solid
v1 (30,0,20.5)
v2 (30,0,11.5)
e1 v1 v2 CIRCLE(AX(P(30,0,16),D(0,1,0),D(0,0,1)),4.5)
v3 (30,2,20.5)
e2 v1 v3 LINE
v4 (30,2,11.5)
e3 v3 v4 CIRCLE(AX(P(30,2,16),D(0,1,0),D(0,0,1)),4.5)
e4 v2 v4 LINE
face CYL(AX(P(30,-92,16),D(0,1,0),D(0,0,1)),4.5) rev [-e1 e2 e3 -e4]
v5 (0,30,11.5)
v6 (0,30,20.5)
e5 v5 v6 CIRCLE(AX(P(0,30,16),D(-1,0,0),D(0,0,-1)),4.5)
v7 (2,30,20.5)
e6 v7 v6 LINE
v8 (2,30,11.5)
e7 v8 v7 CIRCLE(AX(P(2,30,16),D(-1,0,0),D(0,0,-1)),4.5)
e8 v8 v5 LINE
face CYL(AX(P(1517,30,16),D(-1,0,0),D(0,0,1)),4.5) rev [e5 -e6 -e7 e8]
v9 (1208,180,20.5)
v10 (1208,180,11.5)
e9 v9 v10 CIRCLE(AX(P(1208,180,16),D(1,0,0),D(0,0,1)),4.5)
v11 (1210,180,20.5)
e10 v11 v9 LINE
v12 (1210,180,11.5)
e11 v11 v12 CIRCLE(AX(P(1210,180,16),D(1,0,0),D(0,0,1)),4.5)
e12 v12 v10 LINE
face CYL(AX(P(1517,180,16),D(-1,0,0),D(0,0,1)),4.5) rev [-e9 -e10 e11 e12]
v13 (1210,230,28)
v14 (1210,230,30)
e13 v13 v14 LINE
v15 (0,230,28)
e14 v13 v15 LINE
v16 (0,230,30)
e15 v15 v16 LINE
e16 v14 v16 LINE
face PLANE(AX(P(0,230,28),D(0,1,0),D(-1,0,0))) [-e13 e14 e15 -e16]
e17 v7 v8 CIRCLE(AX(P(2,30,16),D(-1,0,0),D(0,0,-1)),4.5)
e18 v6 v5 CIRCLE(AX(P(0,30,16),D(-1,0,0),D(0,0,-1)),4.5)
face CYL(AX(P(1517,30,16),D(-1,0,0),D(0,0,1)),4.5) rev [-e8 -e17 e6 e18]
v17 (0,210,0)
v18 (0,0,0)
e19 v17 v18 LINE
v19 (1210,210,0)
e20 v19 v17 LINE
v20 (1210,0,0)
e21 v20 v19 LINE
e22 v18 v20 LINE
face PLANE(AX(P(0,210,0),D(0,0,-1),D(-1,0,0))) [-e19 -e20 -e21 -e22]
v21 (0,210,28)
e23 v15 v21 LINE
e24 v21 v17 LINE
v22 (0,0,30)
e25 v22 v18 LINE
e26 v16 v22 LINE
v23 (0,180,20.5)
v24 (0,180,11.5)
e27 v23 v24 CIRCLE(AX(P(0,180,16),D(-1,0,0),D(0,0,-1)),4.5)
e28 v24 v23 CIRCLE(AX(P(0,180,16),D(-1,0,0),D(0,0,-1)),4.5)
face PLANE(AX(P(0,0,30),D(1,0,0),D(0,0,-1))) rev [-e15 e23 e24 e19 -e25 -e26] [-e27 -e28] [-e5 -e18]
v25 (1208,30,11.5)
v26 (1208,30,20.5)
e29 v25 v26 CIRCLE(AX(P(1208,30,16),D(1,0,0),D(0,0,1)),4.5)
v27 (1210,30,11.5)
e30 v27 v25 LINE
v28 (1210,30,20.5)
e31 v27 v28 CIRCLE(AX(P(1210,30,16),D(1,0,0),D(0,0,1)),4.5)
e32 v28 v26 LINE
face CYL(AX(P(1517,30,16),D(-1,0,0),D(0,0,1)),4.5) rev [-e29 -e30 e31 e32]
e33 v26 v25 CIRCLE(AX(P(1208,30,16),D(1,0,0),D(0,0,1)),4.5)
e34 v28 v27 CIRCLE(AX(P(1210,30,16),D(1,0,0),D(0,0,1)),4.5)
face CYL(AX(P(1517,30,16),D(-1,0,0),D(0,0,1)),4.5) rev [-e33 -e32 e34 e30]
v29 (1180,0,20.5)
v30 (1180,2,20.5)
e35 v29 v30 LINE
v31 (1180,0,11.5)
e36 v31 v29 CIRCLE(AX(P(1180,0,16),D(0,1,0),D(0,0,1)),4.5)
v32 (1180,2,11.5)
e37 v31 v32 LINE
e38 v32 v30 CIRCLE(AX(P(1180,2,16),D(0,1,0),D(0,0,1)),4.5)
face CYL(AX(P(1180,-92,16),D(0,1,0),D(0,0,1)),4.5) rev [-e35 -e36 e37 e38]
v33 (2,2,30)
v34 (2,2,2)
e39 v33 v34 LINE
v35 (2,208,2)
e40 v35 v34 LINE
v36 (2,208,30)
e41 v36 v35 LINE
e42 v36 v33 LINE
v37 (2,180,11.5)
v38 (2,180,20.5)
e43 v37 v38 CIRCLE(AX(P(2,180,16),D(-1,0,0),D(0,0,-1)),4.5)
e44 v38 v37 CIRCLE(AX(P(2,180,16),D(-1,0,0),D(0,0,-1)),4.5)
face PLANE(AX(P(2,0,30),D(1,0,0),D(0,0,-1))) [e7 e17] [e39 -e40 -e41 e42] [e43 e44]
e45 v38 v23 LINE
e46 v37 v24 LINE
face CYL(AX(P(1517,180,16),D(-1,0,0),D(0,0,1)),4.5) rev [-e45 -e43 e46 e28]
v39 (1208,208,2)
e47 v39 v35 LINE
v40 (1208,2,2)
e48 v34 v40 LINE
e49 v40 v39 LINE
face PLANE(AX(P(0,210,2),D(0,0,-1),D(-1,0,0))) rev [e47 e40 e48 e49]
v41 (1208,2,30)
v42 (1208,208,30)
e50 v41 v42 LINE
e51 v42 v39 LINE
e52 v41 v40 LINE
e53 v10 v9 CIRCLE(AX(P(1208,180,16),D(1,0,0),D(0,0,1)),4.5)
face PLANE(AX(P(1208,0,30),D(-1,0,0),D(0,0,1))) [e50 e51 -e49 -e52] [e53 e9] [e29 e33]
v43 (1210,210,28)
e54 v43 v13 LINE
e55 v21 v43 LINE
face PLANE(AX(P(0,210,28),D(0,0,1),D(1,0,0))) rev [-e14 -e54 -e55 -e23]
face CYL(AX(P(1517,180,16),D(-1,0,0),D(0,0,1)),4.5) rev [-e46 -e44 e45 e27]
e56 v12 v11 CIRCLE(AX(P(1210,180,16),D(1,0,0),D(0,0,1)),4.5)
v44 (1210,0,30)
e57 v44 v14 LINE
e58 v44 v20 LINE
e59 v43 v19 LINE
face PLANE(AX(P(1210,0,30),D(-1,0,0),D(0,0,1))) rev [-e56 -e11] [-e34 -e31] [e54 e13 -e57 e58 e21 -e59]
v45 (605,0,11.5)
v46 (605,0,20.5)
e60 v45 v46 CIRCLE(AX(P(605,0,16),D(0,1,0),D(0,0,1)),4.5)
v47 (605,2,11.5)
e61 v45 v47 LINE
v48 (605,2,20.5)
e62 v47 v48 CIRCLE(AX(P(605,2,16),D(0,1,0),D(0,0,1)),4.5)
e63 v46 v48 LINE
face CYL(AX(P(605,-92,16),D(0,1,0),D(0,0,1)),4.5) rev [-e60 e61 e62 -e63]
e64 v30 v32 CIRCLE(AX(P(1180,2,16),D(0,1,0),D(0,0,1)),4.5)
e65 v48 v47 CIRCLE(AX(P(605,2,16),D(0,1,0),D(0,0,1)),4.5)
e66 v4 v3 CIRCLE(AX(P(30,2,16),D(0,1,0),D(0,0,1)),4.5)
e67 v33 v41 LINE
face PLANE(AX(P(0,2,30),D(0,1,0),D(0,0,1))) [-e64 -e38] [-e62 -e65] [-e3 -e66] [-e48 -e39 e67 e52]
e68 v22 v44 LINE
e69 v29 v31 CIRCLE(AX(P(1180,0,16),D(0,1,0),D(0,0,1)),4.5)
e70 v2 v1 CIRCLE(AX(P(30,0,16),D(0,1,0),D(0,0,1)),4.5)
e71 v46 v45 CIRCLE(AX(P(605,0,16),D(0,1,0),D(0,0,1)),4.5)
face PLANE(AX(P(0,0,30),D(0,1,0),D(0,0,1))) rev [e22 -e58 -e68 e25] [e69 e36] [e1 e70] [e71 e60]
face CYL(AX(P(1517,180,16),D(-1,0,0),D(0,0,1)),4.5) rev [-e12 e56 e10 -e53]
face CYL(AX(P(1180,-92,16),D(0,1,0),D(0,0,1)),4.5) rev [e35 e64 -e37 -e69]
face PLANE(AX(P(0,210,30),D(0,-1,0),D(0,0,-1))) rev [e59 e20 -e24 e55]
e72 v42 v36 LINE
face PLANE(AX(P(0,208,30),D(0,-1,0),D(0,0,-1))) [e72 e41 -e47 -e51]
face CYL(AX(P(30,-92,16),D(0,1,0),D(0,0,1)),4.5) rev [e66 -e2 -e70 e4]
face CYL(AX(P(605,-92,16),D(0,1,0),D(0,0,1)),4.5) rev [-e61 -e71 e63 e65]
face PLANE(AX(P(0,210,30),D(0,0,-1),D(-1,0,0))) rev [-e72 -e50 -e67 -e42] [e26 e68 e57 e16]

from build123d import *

# Parameters (mm, degrees)
SKETCH_1_W               = 1210
SKETCH_1_H               = 210
EXTRUDE_1_DEPTH          = 30
SHELL_1_T                = -2
SKETCH_2_W               = 1210
SKETCH_2_H               = 20
EXTRUDE_2_DEPTH          = 2
SKETCH_3_R               = 4.5
CUT_EXTRUDE_1_DEPTH      = 94
CUT_EXTRUDE_2_DEPTH      = 1515
CUT_EXTRUDE_2_DEPTH_BACK = 94
SKETCH_4_R               = 4.5


with BuildPart() as part:
    # 草图1 → 凸台-拉伸1 (new body)
    with BuildSketch(Plane.XY):
        with Locations((605, 105)):
            Rectangle(SKETCH_1_W, SKETCH_1_H)
    extrude(amount=EXTRUDE_1_DEPTH)

    # 抽壳1
    shell_1_openings = [part.faces().sort_by_distance(p)[0] for p in [
        (605, 105, 30),
    ]]
    offset(amount=SHELL_1_T, openings=shell_1_openings, kind=Kind.INTERSECTION)

    # 草图2 → 凸台-拉伸2 (add)
    with BuildSketch(Plane.XY.offset(30)):
        with Locations((605, 220)):
            Rectangle(SKETCH_2_W, SKETCH_2_H)
    extrude(amount=-EXTRUDE_2_DEPTH)

    # 草图3 → 切除-拉伸1 (cut)
    with BuildSketch(Plane(origin=(0, 2, 0), x_dir=(1, 0, 0), z_dir=(0, 1, 0))):
        with Locations(Location((30, -16, 0), (0, 0, 270))):
            Circle(SKETCH_3_R)
        with Locations(Location((1180, -16, 0), (0, 0, 270))):
            Circle(SKETCH_3_R)
        with Locations(Location((605, -16, 0), (0, 0, 270))):
            Circle(SKETCH_3_R)
    extrude(amount=-CUT_EXTRUDE_1_DEPTH, mode=Mode.SUBTRACT)

    # 草图4 → 切除-拉伸2 (cut, two sides: drawn at the far end of the back side and taken through both)
    with BuildSketch(Plane(origin=(2, 0, 0), x_dir=(0, 0, -1), z_dir=(1, 0, 0)).offset(-CUT_EXTRUDE_2_DEPTH_BACK)):
        with Locations(Location((-16, 180, 0), (0, 0, 180))):
            Circle(SKETCH_4_R)
        with Locations(Location((-16, 30, 0), (0, 0, 180))):
            Circle(SKETCH_4_R)
    extrude(amount=CUT_EXTRUDE_2_DEPTH + CUT_EXTRUDE_2_DEPTH_BACK, mode=Mode.SUBTRACT)


solid = part.part
